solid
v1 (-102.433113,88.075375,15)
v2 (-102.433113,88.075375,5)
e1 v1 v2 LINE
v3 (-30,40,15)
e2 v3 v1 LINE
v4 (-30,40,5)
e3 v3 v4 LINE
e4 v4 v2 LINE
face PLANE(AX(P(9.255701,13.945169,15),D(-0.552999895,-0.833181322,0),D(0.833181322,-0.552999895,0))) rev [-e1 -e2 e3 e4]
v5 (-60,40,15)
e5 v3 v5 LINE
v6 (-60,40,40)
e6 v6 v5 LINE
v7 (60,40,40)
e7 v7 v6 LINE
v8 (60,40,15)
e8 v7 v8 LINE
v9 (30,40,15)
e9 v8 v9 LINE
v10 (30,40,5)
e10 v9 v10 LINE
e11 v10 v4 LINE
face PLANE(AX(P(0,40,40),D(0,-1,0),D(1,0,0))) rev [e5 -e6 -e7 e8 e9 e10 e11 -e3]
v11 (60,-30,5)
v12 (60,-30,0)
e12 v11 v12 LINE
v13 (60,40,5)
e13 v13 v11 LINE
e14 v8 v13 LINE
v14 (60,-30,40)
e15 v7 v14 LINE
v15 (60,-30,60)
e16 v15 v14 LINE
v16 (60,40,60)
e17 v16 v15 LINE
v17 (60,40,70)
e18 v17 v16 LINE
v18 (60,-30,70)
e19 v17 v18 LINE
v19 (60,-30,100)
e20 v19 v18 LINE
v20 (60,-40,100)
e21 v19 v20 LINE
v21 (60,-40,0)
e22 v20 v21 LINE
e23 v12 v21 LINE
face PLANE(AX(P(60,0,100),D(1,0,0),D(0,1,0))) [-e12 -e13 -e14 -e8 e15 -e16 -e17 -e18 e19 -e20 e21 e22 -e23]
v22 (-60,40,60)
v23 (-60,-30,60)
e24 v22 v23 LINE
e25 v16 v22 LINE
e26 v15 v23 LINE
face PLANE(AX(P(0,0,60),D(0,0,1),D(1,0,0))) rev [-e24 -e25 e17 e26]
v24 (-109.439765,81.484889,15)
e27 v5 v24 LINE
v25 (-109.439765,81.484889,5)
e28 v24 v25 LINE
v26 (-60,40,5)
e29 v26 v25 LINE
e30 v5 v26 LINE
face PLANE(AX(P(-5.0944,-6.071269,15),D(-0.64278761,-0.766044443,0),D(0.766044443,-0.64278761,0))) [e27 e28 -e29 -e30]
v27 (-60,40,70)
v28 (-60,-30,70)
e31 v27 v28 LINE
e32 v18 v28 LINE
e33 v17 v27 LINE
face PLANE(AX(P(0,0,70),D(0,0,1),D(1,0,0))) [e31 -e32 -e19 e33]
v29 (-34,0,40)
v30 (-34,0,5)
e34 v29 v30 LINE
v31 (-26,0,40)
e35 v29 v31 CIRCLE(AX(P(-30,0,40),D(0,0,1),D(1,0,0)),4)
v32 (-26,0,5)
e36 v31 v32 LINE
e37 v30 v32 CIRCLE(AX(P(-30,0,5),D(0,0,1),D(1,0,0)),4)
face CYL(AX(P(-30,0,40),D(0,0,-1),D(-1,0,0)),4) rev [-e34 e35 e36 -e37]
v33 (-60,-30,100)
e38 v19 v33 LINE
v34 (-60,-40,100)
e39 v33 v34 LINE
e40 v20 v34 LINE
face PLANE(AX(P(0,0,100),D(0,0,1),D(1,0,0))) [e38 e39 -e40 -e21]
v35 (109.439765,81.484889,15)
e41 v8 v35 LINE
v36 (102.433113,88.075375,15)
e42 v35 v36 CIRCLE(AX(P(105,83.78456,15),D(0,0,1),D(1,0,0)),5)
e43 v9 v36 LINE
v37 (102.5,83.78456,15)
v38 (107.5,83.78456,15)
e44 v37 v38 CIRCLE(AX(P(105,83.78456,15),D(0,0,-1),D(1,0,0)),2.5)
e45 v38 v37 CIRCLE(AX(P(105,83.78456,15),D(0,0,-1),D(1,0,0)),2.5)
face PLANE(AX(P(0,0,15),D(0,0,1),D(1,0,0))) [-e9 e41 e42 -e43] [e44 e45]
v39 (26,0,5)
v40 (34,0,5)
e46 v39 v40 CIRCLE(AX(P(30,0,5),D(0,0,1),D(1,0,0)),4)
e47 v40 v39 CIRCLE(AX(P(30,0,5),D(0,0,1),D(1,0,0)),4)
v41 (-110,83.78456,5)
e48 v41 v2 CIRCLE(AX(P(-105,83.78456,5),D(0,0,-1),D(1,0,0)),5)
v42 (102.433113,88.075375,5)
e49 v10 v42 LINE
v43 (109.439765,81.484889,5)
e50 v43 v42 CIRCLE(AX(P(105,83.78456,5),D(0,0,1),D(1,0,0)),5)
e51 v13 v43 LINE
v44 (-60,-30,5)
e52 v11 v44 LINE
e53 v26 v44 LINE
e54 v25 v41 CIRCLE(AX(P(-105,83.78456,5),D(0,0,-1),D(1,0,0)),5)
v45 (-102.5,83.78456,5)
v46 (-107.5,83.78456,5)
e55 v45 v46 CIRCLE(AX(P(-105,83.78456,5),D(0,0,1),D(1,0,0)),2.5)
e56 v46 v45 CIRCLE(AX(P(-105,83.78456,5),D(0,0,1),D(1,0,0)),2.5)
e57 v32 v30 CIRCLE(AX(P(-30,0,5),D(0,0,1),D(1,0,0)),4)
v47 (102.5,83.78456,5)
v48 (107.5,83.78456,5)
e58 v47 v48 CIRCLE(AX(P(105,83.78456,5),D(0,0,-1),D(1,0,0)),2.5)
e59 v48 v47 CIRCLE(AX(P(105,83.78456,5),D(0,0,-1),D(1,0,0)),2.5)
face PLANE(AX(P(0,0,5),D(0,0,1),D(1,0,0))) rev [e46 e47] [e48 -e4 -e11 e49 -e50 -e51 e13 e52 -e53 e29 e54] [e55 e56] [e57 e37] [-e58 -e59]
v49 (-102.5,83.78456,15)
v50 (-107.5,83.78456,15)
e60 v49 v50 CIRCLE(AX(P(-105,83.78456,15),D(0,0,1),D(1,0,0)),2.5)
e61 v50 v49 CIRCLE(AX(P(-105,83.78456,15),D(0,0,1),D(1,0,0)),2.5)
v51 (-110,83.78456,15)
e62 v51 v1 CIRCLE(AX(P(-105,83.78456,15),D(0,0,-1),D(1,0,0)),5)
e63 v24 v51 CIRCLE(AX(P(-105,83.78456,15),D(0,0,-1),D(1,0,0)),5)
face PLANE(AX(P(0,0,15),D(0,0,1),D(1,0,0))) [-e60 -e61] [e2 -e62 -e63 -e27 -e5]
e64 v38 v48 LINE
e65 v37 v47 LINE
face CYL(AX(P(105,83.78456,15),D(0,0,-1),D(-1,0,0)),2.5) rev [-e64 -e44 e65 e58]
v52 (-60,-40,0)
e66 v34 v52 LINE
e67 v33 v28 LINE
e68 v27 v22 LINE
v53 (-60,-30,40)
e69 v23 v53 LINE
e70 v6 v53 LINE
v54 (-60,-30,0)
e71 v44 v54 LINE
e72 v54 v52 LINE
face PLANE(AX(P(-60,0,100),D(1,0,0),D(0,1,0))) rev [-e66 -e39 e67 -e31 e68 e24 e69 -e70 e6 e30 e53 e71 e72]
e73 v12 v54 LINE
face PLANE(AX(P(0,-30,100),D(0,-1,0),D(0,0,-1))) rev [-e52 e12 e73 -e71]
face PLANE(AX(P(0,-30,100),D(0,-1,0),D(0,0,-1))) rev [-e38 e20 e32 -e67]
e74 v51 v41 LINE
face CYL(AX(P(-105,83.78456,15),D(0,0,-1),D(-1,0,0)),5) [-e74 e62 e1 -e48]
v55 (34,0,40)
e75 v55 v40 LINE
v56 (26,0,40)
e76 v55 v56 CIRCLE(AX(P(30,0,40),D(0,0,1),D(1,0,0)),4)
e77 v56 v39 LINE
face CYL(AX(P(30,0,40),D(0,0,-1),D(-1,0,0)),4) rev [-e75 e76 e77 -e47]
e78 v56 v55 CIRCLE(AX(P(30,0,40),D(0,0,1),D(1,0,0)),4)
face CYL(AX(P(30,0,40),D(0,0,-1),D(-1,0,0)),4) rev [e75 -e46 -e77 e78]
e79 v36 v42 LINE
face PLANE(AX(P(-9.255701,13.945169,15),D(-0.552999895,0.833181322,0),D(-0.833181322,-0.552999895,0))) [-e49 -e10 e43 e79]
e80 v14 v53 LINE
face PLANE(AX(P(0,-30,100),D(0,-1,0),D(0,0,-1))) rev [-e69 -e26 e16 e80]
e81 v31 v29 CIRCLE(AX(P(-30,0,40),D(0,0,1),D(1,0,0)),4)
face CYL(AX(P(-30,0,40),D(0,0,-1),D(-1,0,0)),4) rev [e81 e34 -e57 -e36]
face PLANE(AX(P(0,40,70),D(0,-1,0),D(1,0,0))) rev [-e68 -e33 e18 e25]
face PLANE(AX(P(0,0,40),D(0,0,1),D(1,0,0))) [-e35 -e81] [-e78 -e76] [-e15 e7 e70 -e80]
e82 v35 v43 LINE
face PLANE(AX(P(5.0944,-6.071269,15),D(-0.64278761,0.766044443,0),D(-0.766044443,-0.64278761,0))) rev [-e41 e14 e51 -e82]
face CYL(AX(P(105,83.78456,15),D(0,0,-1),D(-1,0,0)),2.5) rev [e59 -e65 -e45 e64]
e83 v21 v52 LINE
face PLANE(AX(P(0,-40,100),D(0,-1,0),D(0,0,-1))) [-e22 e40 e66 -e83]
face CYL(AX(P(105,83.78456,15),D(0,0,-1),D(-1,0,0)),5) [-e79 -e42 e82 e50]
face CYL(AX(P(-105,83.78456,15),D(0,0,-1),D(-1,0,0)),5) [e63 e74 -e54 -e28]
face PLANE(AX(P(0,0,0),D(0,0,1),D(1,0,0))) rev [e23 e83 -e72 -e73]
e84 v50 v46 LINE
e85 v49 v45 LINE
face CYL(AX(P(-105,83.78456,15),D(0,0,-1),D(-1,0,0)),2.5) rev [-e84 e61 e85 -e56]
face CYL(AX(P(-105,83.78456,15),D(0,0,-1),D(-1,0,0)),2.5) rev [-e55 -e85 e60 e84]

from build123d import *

# Parameters (mm, degrees)
SIDE_PROFILE_SKETCH_W            = 120
SIDE_PROFILE_SKETCH_H            = 10
MAIN_BODY_EXTRUDE_100_DEPTH      = 100
UPRIGHT_START                    = 5
SKETCH1_5_R                      = 2.5
SKETCH1_5_W                      = 120
SKETCH1_5_H                      = 80
SKETCH1_5_R_2                    = 4
UPRIGHT_BLOCK_EXTRUDE_35_DEPTH   = 35
FRONT_START                      = 5
SKETCH1_6_R                      = 2.5
FRONT_LEVER_ARM_EXTRUDE_10_DEPTH = 10
REAR_START                       = 60
SKETCH1_7_W                      = 120
SKETCH1_7_H                      = 70
REAR_LEVER_ARM_EXTRUDE_10_DEPTH  = 10


with BuildPart() as part:
    # Side Profile Sketch → Main Body Extrude 100 (new body)
    with BuildSketch(Plane.XY):
        with Locations((0, -35)):
            Rectangle(SIDE_PROFILE_SKETCH_W, SIDE_PROFILE_SKETCH_H)
    extrude(amount=MAIN_BODY_EXTRUDE_100_DEPTH)

    # Sketch1_5 → Upright Block Extrude 35 (add)
    # profile 1 of 3: a face of its own
    with BuildSketch(Plane.XY.offset(UPRIGHT_START)):
        with Locations((-105, 83.784559584)):
            Circle(SKETCH1_5_R)
    # profile 2 of 3: a face of its own
    with BuildSketch(Plane.XY.offset(UPRIGHT_START)):
        with Locations((105, 83.784559584)):
            Circle(SKETCH1_5_R)
    # profile 3 of 3: a face of its own
    with BuildSketch(Plane.XY.offset(UPRIGHT_START)):
        Rectangle(SKETCH1_5_W, SKETCH1_5_H)
        with Locations((-30, 0)):
            Circle(SKETCH1_5_R_2, mode=Mode.SUBTRACT)
        with Locations((30, 0)):
            Circle(SKETCH1_5_R_2, mode=Mode.SUBTRACT)
    extrude(amount=UPRIGHT_BLOCK_EXTRUDE_35_DEPTH)


with BuildPart() as upright_block_extrude_35_kept_piece:
    # of the separate pieces the step leaves, the one the design keeps (upright_block_extrude_35_pieces_kept)
    add(part.part.solids().sort_by_distance((60, -30, 0))[0])

    # Sketch1_6 → Front Lever Arm Extrude 10 (add)
    # profile 1 of 2: a face of its own
    with BuildSketch(Plane.XY.offset(FRONT_START)):
        with BuildLine():
            Line((102.433113428, 88.075374579), (30, 40))
            Line((30, 40), (60, 40))
            Line((60, 40), (109.439765001, 81.484888578))
            ThreePointArc((109.439765001, 81.484888578), (108.425718149, 87.426599557), (102.433113428, 88.075374579))
        make_face()
        with Locations((105, 83.784559584)):
            Circle(SKETCH1_6_R, mode=Mode.SUBTRACT)
    # profile 2 of 2: a face of its own
    with BuildSketch(Plane.XY.offset(FRONT_START)):
        with BuildLine():
            Line((-109.439765001, 81.484888578), (-60, 40))
            Line((-60, 40), (-30, 40))
            Line((-30, 40), (-102.433113428, 88.075374579))
            ThreePointArc((-102.433113428, 88.075374579), (-108.425718149, 87.426599557), (-109.439765001, 81.484888578))
        make_face()
        with Locations((-105, 83.784559584)):
            Circle(SKETCH1_6_R, mode=Mode.SUBTRACT)
    extrude(amount=FRONT_LEVER_ARM_EXTRUDE_10_DEPTH)

    # Sketch1_7 → Rear Lever Arm Extrude 10 (add)
    with BuildSketch(Plane.XY.offset(REAR_START)):
        with Locations((0, 5)):
            Rectangle(SKETCH1_7_W, SKETCH1_7_H)
    extrude(amount=REAR_LEVER_ARM_EXTRUDE_10_DEPTH)


solid = upright_block_extrude_35_kept_piece.part
